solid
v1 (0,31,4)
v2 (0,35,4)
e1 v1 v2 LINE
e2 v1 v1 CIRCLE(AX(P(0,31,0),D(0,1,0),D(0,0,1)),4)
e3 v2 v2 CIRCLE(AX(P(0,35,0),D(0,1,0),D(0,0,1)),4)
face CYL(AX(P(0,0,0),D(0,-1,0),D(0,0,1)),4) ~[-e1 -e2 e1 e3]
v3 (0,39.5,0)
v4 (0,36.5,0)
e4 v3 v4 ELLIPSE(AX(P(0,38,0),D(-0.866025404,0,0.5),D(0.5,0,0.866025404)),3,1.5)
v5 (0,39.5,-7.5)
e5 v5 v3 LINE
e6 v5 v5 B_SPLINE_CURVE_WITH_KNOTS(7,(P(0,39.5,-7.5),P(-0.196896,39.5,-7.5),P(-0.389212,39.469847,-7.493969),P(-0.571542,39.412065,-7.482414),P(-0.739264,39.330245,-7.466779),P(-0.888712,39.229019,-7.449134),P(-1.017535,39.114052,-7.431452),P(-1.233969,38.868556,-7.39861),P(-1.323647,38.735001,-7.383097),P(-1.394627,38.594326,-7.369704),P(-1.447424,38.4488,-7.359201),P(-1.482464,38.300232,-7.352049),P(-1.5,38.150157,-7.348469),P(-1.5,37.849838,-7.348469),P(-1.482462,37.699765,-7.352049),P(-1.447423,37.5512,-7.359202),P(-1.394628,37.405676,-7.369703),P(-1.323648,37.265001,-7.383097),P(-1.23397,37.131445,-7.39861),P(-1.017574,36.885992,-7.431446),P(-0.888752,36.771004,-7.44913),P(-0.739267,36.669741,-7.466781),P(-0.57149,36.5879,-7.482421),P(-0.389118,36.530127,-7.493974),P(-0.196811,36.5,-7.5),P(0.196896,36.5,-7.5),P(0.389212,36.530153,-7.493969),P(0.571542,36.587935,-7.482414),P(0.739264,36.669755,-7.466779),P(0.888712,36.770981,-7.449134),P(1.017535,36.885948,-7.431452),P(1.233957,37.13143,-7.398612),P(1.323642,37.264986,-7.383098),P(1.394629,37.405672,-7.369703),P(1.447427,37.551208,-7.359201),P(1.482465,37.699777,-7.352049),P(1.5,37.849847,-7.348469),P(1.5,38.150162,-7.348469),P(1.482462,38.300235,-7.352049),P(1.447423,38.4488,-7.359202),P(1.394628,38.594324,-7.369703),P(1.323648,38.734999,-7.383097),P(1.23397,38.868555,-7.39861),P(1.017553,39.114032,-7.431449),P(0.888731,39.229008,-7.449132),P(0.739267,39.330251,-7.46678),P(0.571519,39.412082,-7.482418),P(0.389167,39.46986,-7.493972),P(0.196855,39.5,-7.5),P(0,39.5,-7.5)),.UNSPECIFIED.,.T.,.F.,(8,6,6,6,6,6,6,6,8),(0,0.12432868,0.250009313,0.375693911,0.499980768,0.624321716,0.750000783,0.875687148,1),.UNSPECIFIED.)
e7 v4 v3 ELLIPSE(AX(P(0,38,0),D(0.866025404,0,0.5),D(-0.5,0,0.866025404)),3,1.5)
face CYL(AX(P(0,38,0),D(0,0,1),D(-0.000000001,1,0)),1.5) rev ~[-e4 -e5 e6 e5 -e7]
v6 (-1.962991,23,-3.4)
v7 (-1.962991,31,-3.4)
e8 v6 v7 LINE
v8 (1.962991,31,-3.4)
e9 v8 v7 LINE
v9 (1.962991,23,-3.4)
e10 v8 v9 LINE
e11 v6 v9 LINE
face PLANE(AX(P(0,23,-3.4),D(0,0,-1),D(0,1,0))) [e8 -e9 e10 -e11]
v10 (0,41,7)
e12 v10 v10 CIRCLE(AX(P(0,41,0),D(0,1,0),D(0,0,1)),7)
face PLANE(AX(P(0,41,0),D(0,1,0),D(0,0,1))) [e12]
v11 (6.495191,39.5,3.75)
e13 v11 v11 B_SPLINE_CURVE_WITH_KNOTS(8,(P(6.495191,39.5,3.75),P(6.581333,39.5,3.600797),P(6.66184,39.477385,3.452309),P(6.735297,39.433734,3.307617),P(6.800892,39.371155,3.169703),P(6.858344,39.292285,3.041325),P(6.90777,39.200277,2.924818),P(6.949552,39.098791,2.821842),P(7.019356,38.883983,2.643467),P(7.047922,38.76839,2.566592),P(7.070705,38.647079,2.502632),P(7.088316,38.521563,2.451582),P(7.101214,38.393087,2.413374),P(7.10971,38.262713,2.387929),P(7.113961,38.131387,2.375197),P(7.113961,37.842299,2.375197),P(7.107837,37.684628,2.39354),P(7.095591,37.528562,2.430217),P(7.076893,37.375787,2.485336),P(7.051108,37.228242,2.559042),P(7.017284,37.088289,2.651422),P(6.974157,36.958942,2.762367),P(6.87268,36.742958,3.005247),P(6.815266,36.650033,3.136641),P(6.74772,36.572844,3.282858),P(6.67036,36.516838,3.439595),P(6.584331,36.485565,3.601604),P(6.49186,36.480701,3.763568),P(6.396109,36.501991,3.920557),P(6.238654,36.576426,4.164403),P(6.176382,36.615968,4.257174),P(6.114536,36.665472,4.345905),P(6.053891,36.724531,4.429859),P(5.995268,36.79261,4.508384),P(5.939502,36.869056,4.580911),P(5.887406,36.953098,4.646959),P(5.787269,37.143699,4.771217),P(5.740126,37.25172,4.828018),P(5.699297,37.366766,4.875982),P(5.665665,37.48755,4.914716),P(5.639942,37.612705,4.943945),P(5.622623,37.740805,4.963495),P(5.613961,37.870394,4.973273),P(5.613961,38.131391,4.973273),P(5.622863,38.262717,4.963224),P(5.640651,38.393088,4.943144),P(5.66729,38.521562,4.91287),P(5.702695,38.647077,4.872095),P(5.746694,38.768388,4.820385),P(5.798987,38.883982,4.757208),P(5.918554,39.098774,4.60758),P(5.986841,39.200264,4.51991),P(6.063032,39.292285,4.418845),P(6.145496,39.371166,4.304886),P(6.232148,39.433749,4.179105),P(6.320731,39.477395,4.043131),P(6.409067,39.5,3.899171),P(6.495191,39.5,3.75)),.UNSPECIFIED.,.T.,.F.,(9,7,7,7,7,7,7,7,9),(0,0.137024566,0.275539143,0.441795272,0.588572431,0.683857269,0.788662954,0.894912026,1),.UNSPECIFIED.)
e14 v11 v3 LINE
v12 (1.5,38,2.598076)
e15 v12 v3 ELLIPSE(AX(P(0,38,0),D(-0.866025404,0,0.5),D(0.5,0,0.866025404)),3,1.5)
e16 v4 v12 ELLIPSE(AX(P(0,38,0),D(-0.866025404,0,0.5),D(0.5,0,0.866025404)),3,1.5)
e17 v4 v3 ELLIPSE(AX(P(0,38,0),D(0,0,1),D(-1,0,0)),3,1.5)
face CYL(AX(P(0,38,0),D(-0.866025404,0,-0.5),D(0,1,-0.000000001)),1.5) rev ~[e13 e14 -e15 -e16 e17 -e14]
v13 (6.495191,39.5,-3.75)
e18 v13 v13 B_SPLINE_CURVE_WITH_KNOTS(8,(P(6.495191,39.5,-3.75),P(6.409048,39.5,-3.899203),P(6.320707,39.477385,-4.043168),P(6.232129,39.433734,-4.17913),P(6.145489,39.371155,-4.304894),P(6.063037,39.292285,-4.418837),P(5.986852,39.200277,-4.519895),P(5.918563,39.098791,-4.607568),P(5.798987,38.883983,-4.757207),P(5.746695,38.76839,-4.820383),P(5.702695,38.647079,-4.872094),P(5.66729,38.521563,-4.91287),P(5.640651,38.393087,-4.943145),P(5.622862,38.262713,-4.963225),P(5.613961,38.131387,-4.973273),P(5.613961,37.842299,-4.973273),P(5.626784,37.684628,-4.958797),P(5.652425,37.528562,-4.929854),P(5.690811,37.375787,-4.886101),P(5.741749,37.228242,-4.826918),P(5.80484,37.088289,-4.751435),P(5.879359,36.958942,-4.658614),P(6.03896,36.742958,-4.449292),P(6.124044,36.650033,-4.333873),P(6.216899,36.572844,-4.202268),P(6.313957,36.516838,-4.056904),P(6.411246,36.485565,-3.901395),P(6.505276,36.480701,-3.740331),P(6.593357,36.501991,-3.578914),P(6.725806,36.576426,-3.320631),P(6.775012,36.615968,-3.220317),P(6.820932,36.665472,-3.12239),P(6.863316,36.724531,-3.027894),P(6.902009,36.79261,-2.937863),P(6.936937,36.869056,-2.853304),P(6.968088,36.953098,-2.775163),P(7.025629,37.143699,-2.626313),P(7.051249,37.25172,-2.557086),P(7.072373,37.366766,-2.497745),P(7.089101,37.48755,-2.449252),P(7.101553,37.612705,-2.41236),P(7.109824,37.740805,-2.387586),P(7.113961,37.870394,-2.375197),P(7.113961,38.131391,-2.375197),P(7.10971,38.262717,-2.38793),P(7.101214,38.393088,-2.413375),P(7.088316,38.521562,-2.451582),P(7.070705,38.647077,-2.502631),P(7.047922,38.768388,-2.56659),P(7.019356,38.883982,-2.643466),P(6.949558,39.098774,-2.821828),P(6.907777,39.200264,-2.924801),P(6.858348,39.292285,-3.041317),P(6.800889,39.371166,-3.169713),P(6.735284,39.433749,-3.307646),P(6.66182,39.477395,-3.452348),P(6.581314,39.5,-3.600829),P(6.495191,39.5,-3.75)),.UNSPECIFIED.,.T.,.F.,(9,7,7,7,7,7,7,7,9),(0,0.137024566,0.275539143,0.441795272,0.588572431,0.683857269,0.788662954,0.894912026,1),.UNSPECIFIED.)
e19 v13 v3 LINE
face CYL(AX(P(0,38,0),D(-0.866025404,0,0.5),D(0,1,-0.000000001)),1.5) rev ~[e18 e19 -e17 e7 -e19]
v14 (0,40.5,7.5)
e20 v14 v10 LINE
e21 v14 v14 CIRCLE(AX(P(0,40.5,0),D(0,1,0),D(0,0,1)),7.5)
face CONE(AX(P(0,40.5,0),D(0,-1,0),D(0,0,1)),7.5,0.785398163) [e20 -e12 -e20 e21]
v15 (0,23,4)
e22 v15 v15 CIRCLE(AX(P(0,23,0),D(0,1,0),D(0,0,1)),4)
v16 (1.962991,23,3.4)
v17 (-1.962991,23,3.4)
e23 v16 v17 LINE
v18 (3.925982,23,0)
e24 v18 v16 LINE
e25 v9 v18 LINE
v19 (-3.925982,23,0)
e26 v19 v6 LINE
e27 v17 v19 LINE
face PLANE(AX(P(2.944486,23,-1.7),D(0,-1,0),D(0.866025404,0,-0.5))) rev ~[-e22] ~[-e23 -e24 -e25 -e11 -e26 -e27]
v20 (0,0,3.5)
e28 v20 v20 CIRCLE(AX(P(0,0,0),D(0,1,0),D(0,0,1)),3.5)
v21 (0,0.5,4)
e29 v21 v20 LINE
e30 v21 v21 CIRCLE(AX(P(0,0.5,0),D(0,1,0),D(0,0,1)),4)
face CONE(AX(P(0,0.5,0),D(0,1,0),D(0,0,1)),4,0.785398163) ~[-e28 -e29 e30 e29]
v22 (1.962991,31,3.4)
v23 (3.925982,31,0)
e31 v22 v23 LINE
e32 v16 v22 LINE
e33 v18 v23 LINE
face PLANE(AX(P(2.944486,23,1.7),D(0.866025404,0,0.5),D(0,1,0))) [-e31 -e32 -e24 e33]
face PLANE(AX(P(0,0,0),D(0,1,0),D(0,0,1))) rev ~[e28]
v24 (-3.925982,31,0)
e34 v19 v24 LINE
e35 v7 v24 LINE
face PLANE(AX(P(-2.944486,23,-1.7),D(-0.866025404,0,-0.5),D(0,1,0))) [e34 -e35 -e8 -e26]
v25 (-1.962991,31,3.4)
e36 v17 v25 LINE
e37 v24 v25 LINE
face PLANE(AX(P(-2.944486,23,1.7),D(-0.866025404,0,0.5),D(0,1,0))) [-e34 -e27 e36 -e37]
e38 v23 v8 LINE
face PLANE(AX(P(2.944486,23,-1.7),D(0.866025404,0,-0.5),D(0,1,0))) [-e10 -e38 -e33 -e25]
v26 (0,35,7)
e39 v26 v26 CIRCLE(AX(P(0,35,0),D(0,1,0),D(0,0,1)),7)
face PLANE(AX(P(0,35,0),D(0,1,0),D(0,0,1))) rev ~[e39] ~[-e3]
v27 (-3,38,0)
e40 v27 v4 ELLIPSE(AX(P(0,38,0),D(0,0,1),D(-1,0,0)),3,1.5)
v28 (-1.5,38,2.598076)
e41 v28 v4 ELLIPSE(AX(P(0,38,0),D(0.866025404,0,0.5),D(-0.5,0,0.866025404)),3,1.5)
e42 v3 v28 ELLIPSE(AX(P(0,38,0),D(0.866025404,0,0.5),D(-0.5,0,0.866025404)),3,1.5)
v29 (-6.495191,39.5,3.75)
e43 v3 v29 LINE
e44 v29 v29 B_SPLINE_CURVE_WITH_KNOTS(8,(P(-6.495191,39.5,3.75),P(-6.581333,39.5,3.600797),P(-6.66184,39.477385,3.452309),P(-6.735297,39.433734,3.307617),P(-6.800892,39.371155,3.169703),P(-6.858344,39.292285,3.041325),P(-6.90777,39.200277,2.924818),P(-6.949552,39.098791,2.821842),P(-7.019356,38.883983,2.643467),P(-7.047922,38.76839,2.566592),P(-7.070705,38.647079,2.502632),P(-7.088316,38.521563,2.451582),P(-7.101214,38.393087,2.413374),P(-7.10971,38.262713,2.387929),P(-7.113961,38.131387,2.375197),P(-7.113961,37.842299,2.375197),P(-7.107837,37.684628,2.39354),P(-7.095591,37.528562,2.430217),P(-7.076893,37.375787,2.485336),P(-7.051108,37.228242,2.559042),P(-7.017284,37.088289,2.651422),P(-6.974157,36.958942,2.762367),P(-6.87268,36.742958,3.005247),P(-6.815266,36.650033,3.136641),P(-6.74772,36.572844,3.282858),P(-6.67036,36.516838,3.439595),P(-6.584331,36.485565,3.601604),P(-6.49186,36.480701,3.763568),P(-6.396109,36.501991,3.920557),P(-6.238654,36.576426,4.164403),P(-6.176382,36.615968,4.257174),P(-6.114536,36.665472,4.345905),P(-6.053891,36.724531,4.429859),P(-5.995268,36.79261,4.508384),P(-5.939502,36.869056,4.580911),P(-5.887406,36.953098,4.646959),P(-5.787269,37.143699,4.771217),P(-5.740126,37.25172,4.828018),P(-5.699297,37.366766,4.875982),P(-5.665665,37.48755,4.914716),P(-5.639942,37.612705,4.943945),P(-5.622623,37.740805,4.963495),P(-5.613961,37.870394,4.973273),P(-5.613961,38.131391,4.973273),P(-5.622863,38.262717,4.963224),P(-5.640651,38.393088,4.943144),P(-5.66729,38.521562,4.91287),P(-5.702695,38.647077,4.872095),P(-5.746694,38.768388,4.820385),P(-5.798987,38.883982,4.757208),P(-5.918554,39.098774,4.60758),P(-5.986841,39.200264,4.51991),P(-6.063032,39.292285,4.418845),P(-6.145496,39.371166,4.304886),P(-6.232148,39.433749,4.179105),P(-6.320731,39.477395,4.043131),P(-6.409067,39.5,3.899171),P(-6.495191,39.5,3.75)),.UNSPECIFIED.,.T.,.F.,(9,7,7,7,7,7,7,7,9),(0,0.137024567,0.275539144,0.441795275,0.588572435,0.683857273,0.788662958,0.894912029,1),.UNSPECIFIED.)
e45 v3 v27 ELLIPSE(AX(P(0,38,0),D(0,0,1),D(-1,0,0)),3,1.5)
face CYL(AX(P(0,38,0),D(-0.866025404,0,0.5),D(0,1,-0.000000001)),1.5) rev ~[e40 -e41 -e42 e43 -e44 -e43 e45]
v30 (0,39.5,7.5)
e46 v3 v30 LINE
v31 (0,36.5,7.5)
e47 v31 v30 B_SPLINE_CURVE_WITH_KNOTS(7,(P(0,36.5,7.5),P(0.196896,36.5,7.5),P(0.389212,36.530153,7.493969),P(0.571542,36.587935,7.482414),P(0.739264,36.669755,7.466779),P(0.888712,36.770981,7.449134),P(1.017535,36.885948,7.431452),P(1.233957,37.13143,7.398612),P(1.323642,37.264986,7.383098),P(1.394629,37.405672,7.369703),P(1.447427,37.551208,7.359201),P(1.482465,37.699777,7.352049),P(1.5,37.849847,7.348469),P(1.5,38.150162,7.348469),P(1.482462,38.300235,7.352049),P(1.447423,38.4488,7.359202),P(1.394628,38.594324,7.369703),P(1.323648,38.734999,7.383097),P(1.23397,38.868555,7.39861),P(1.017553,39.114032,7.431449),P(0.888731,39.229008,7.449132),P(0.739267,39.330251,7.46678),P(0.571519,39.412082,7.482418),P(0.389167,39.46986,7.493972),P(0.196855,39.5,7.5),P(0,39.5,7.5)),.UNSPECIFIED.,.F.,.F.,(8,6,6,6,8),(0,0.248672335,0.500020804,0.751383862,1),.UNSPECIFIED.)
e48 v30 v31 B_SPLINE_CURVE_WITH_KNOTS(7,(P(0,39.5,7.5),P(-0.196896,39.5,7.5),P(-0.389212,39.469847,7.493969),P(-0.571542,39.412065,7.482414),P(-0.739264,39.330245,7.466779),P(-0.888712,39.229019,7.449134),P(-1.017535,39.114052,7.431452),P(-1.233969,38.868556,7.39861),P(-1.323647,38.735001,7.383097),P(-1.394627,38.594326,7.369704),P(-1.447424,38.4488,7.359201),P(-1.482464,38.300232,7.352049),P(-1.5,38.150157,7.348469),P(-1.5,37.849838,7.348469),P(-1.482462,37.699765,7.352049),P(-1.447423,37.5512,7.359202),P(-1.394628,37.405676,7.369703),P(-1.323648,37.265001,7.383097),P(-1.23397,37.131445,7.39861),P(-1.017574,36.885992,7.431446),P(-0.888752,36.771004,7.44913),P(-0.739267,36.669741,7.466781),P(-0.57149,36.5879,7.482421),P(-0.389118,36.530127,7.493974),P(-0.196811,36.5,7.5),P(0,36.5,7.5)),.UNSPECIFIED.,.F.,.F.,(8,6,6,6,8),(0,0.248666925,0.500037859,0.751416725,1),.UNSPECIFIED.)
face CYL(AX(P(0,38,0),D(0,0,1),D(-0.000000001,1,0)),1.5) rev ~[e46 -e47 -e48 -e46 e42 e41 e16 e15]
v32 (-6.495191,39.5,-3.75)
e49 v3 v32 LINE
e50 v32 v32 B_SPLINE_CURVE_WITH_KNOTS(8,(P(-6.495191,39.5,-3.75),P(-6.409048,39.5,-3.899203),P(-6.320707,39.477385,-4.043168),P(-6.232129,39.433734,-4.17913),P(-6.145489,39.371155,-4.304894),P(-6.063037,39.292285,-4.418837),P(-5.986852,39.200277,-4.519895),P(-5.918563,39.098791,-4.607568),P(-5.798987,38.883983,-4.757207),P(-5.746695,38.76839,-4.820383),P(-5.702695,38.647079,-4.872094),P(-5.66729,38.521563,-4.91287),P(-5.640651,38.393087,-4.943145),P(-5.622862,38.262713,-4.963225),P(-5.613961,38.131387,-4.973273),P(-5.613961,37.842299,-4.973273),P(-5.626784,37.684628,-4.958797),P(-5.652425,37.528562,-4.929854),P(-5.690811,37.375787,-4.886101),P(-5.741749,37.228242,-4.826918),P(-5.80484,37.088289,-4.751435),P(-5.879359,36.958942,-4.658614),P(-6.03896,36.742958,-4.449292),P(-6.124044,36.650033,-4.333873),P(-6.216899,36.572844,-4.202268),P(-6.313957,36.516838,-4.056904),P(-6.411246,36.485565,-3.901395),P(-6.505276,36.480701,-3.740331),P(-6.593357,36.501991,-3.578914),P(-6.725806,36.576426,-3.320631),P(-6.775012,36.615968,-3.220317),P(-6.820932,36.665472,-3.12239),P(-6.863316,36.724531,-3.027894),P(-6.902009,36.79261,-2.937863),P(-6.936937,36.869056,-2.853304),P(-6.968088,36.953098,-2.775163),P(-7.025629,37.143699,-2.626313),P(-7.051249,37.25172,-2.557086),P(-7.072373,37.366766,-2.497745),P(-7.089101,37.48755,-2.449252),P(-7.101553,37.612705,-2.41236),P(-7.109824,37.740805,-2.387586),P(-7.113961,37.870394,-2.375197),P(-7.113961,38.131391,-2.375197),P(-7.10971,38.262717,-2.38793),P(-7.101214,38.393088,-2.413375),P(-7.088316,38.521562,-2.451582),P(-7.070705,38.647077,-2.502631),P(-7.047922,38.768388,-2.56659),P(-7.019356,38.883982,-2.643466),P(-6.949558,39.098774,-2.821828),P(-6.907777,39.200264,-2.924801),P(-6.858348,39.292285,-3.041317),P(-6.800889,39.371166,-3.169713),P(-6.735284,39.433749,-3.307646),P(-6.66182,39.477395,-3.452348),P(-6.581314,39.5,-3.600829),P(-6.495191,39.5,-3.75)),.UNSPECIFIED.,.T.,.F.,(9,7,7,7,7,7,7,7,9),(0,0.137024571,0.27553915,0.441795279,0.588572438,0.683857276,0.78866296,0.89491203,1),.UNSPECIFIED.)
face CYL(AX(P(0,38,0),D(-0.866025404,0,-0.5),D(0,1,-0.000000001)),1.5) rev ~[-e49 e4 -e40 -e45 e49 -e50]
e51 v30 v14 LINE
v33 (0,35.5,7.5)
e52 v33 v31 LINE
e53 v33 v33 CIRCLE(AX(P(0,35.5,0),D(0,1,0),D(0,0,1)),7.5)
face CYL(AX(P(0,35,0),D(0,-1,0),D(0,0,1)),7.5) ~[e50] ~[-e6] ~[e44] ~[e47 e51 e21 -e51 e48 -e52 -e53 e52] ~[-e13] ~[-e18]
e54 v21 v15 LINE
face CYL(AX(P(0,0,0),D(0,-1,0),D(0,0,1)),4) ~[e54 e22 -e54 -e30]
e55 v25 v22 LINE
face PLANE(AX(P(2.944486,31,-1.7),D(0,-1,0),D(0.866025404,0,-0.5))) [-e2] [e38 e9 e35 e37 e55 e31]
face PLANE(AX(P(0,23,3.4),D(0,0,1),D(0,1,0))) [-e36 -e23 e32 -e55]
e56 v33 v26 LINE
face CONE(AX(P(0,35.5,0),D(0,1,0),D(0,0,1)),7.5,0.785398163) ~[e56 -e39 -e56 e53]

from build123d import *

# Parameters (mm, degrees)
SKETCH1_R           = 4
BOSS_EXTRUDE1_DEPTH = 35
SKETCH2_R           = 7.5
BOSS_EXTRUDE2_DEPTH = 6
CHAMFER1_SIZE       = 0.5
SKETCH3_R           = 1.5
CUT_EXTRUDE1_DEPTH  = 9.5
CIRPATTERN1_COUNT   = 6
SKETCH5_W           = 1.2
SKETCH5_H           = 8
CUT_EXTRUDE3_DEPTH  = 5
CIRPATTERN3_COUNT   = 6


with BuildPart() as part:
    # Sketch1 → Boss-Extrude1 (new body)
    with BuildSketch(Plane(origin=(0, 0, 0), x_dir=(1, 0, 0), z_dir=(0, 1, 0))):
        with Locations(Location((0, 0, 0), (0, 0, 270))):
            Circle(SKETCH1_R)
    extrude(amount=BOSS_EXTRUDE1_DEPTH)

    # Sketch2 → Boss-Extrude2 (add)
    with BuildSketch(Plane(origin=(0, 35, 0), x_dir=(1, 0, 0), z_dir=(0, 1, 0))):
        with Locations(Location((0, 0, 0), (0, 0, 270))):
            Circle(SKETCH2_R)
    extrude(amount=BOSS_EXTRUDE2_DEPTH)

    # Chamfer1
    chamfer1_edges = [part.edges().sort_by_distance(p)[0] for p in [
        (0, 0, -4),
        (0, 35, -7.5),
        (0, 41, -7.5),
    ]]
    chamfer(chamfer1_edges, length=CHAMFER1_SIZE)

    # Sketch3 → Cut-Extrude1 (cut, symmetric)
    with BuildSketch(Plane.XY):
        with Locations(Location((0, 38, 0), (0, 0, 90.000000044))):
            Circle(SKETCH3_R)
    cut_extrude1 = extrude(amount=CUT_EXTRUDE1_DEPTH, both=True, mode=Mode.SUBTRACT)

    # CirPattern1: Cut-Extrude1 ×6 about axis
    cirpattern1_axis = Axis((0, 41, 0), (0, -1, 0))
    for i in range(1, CIRPATTERN1_COUNT):
        add(cut_extrude1.rotate(cirpattern1_axis, i * 360 / CIRPATTERN1_COUNT), mode=Mode.SUBTRACT)

    # Sketch5 → Cut-Extrude3 (cut, symmetric)
    with BuildSketch(Plane(origin=(0, 0, 0), x_dir=(0, 0, -1), z_dir=(1, 0, 0))):
        with Locations((4, 27)):
            Rectangle(SKETCH5_W, SKETCH5_H)
    cut_extrude3 = extrude(amount=CUT_EXTRUDE3_DEPTH, both=True, mode=Mode.SUBTRACT)

    # CirPattern3: Cut-Extrude3 ×6 about axis
    cirpattern3_axis = Axis((0, 0, 0), (0, 1, 0))
    for i in range(1, CIRPATTERN3_COUNT):
        add(cut_extrude3.rotate(cirpattern3_axis, i * 360 / CIRPATTERN3_COUNT), mode=Mode.SUBTRACT)


solid = part.part
